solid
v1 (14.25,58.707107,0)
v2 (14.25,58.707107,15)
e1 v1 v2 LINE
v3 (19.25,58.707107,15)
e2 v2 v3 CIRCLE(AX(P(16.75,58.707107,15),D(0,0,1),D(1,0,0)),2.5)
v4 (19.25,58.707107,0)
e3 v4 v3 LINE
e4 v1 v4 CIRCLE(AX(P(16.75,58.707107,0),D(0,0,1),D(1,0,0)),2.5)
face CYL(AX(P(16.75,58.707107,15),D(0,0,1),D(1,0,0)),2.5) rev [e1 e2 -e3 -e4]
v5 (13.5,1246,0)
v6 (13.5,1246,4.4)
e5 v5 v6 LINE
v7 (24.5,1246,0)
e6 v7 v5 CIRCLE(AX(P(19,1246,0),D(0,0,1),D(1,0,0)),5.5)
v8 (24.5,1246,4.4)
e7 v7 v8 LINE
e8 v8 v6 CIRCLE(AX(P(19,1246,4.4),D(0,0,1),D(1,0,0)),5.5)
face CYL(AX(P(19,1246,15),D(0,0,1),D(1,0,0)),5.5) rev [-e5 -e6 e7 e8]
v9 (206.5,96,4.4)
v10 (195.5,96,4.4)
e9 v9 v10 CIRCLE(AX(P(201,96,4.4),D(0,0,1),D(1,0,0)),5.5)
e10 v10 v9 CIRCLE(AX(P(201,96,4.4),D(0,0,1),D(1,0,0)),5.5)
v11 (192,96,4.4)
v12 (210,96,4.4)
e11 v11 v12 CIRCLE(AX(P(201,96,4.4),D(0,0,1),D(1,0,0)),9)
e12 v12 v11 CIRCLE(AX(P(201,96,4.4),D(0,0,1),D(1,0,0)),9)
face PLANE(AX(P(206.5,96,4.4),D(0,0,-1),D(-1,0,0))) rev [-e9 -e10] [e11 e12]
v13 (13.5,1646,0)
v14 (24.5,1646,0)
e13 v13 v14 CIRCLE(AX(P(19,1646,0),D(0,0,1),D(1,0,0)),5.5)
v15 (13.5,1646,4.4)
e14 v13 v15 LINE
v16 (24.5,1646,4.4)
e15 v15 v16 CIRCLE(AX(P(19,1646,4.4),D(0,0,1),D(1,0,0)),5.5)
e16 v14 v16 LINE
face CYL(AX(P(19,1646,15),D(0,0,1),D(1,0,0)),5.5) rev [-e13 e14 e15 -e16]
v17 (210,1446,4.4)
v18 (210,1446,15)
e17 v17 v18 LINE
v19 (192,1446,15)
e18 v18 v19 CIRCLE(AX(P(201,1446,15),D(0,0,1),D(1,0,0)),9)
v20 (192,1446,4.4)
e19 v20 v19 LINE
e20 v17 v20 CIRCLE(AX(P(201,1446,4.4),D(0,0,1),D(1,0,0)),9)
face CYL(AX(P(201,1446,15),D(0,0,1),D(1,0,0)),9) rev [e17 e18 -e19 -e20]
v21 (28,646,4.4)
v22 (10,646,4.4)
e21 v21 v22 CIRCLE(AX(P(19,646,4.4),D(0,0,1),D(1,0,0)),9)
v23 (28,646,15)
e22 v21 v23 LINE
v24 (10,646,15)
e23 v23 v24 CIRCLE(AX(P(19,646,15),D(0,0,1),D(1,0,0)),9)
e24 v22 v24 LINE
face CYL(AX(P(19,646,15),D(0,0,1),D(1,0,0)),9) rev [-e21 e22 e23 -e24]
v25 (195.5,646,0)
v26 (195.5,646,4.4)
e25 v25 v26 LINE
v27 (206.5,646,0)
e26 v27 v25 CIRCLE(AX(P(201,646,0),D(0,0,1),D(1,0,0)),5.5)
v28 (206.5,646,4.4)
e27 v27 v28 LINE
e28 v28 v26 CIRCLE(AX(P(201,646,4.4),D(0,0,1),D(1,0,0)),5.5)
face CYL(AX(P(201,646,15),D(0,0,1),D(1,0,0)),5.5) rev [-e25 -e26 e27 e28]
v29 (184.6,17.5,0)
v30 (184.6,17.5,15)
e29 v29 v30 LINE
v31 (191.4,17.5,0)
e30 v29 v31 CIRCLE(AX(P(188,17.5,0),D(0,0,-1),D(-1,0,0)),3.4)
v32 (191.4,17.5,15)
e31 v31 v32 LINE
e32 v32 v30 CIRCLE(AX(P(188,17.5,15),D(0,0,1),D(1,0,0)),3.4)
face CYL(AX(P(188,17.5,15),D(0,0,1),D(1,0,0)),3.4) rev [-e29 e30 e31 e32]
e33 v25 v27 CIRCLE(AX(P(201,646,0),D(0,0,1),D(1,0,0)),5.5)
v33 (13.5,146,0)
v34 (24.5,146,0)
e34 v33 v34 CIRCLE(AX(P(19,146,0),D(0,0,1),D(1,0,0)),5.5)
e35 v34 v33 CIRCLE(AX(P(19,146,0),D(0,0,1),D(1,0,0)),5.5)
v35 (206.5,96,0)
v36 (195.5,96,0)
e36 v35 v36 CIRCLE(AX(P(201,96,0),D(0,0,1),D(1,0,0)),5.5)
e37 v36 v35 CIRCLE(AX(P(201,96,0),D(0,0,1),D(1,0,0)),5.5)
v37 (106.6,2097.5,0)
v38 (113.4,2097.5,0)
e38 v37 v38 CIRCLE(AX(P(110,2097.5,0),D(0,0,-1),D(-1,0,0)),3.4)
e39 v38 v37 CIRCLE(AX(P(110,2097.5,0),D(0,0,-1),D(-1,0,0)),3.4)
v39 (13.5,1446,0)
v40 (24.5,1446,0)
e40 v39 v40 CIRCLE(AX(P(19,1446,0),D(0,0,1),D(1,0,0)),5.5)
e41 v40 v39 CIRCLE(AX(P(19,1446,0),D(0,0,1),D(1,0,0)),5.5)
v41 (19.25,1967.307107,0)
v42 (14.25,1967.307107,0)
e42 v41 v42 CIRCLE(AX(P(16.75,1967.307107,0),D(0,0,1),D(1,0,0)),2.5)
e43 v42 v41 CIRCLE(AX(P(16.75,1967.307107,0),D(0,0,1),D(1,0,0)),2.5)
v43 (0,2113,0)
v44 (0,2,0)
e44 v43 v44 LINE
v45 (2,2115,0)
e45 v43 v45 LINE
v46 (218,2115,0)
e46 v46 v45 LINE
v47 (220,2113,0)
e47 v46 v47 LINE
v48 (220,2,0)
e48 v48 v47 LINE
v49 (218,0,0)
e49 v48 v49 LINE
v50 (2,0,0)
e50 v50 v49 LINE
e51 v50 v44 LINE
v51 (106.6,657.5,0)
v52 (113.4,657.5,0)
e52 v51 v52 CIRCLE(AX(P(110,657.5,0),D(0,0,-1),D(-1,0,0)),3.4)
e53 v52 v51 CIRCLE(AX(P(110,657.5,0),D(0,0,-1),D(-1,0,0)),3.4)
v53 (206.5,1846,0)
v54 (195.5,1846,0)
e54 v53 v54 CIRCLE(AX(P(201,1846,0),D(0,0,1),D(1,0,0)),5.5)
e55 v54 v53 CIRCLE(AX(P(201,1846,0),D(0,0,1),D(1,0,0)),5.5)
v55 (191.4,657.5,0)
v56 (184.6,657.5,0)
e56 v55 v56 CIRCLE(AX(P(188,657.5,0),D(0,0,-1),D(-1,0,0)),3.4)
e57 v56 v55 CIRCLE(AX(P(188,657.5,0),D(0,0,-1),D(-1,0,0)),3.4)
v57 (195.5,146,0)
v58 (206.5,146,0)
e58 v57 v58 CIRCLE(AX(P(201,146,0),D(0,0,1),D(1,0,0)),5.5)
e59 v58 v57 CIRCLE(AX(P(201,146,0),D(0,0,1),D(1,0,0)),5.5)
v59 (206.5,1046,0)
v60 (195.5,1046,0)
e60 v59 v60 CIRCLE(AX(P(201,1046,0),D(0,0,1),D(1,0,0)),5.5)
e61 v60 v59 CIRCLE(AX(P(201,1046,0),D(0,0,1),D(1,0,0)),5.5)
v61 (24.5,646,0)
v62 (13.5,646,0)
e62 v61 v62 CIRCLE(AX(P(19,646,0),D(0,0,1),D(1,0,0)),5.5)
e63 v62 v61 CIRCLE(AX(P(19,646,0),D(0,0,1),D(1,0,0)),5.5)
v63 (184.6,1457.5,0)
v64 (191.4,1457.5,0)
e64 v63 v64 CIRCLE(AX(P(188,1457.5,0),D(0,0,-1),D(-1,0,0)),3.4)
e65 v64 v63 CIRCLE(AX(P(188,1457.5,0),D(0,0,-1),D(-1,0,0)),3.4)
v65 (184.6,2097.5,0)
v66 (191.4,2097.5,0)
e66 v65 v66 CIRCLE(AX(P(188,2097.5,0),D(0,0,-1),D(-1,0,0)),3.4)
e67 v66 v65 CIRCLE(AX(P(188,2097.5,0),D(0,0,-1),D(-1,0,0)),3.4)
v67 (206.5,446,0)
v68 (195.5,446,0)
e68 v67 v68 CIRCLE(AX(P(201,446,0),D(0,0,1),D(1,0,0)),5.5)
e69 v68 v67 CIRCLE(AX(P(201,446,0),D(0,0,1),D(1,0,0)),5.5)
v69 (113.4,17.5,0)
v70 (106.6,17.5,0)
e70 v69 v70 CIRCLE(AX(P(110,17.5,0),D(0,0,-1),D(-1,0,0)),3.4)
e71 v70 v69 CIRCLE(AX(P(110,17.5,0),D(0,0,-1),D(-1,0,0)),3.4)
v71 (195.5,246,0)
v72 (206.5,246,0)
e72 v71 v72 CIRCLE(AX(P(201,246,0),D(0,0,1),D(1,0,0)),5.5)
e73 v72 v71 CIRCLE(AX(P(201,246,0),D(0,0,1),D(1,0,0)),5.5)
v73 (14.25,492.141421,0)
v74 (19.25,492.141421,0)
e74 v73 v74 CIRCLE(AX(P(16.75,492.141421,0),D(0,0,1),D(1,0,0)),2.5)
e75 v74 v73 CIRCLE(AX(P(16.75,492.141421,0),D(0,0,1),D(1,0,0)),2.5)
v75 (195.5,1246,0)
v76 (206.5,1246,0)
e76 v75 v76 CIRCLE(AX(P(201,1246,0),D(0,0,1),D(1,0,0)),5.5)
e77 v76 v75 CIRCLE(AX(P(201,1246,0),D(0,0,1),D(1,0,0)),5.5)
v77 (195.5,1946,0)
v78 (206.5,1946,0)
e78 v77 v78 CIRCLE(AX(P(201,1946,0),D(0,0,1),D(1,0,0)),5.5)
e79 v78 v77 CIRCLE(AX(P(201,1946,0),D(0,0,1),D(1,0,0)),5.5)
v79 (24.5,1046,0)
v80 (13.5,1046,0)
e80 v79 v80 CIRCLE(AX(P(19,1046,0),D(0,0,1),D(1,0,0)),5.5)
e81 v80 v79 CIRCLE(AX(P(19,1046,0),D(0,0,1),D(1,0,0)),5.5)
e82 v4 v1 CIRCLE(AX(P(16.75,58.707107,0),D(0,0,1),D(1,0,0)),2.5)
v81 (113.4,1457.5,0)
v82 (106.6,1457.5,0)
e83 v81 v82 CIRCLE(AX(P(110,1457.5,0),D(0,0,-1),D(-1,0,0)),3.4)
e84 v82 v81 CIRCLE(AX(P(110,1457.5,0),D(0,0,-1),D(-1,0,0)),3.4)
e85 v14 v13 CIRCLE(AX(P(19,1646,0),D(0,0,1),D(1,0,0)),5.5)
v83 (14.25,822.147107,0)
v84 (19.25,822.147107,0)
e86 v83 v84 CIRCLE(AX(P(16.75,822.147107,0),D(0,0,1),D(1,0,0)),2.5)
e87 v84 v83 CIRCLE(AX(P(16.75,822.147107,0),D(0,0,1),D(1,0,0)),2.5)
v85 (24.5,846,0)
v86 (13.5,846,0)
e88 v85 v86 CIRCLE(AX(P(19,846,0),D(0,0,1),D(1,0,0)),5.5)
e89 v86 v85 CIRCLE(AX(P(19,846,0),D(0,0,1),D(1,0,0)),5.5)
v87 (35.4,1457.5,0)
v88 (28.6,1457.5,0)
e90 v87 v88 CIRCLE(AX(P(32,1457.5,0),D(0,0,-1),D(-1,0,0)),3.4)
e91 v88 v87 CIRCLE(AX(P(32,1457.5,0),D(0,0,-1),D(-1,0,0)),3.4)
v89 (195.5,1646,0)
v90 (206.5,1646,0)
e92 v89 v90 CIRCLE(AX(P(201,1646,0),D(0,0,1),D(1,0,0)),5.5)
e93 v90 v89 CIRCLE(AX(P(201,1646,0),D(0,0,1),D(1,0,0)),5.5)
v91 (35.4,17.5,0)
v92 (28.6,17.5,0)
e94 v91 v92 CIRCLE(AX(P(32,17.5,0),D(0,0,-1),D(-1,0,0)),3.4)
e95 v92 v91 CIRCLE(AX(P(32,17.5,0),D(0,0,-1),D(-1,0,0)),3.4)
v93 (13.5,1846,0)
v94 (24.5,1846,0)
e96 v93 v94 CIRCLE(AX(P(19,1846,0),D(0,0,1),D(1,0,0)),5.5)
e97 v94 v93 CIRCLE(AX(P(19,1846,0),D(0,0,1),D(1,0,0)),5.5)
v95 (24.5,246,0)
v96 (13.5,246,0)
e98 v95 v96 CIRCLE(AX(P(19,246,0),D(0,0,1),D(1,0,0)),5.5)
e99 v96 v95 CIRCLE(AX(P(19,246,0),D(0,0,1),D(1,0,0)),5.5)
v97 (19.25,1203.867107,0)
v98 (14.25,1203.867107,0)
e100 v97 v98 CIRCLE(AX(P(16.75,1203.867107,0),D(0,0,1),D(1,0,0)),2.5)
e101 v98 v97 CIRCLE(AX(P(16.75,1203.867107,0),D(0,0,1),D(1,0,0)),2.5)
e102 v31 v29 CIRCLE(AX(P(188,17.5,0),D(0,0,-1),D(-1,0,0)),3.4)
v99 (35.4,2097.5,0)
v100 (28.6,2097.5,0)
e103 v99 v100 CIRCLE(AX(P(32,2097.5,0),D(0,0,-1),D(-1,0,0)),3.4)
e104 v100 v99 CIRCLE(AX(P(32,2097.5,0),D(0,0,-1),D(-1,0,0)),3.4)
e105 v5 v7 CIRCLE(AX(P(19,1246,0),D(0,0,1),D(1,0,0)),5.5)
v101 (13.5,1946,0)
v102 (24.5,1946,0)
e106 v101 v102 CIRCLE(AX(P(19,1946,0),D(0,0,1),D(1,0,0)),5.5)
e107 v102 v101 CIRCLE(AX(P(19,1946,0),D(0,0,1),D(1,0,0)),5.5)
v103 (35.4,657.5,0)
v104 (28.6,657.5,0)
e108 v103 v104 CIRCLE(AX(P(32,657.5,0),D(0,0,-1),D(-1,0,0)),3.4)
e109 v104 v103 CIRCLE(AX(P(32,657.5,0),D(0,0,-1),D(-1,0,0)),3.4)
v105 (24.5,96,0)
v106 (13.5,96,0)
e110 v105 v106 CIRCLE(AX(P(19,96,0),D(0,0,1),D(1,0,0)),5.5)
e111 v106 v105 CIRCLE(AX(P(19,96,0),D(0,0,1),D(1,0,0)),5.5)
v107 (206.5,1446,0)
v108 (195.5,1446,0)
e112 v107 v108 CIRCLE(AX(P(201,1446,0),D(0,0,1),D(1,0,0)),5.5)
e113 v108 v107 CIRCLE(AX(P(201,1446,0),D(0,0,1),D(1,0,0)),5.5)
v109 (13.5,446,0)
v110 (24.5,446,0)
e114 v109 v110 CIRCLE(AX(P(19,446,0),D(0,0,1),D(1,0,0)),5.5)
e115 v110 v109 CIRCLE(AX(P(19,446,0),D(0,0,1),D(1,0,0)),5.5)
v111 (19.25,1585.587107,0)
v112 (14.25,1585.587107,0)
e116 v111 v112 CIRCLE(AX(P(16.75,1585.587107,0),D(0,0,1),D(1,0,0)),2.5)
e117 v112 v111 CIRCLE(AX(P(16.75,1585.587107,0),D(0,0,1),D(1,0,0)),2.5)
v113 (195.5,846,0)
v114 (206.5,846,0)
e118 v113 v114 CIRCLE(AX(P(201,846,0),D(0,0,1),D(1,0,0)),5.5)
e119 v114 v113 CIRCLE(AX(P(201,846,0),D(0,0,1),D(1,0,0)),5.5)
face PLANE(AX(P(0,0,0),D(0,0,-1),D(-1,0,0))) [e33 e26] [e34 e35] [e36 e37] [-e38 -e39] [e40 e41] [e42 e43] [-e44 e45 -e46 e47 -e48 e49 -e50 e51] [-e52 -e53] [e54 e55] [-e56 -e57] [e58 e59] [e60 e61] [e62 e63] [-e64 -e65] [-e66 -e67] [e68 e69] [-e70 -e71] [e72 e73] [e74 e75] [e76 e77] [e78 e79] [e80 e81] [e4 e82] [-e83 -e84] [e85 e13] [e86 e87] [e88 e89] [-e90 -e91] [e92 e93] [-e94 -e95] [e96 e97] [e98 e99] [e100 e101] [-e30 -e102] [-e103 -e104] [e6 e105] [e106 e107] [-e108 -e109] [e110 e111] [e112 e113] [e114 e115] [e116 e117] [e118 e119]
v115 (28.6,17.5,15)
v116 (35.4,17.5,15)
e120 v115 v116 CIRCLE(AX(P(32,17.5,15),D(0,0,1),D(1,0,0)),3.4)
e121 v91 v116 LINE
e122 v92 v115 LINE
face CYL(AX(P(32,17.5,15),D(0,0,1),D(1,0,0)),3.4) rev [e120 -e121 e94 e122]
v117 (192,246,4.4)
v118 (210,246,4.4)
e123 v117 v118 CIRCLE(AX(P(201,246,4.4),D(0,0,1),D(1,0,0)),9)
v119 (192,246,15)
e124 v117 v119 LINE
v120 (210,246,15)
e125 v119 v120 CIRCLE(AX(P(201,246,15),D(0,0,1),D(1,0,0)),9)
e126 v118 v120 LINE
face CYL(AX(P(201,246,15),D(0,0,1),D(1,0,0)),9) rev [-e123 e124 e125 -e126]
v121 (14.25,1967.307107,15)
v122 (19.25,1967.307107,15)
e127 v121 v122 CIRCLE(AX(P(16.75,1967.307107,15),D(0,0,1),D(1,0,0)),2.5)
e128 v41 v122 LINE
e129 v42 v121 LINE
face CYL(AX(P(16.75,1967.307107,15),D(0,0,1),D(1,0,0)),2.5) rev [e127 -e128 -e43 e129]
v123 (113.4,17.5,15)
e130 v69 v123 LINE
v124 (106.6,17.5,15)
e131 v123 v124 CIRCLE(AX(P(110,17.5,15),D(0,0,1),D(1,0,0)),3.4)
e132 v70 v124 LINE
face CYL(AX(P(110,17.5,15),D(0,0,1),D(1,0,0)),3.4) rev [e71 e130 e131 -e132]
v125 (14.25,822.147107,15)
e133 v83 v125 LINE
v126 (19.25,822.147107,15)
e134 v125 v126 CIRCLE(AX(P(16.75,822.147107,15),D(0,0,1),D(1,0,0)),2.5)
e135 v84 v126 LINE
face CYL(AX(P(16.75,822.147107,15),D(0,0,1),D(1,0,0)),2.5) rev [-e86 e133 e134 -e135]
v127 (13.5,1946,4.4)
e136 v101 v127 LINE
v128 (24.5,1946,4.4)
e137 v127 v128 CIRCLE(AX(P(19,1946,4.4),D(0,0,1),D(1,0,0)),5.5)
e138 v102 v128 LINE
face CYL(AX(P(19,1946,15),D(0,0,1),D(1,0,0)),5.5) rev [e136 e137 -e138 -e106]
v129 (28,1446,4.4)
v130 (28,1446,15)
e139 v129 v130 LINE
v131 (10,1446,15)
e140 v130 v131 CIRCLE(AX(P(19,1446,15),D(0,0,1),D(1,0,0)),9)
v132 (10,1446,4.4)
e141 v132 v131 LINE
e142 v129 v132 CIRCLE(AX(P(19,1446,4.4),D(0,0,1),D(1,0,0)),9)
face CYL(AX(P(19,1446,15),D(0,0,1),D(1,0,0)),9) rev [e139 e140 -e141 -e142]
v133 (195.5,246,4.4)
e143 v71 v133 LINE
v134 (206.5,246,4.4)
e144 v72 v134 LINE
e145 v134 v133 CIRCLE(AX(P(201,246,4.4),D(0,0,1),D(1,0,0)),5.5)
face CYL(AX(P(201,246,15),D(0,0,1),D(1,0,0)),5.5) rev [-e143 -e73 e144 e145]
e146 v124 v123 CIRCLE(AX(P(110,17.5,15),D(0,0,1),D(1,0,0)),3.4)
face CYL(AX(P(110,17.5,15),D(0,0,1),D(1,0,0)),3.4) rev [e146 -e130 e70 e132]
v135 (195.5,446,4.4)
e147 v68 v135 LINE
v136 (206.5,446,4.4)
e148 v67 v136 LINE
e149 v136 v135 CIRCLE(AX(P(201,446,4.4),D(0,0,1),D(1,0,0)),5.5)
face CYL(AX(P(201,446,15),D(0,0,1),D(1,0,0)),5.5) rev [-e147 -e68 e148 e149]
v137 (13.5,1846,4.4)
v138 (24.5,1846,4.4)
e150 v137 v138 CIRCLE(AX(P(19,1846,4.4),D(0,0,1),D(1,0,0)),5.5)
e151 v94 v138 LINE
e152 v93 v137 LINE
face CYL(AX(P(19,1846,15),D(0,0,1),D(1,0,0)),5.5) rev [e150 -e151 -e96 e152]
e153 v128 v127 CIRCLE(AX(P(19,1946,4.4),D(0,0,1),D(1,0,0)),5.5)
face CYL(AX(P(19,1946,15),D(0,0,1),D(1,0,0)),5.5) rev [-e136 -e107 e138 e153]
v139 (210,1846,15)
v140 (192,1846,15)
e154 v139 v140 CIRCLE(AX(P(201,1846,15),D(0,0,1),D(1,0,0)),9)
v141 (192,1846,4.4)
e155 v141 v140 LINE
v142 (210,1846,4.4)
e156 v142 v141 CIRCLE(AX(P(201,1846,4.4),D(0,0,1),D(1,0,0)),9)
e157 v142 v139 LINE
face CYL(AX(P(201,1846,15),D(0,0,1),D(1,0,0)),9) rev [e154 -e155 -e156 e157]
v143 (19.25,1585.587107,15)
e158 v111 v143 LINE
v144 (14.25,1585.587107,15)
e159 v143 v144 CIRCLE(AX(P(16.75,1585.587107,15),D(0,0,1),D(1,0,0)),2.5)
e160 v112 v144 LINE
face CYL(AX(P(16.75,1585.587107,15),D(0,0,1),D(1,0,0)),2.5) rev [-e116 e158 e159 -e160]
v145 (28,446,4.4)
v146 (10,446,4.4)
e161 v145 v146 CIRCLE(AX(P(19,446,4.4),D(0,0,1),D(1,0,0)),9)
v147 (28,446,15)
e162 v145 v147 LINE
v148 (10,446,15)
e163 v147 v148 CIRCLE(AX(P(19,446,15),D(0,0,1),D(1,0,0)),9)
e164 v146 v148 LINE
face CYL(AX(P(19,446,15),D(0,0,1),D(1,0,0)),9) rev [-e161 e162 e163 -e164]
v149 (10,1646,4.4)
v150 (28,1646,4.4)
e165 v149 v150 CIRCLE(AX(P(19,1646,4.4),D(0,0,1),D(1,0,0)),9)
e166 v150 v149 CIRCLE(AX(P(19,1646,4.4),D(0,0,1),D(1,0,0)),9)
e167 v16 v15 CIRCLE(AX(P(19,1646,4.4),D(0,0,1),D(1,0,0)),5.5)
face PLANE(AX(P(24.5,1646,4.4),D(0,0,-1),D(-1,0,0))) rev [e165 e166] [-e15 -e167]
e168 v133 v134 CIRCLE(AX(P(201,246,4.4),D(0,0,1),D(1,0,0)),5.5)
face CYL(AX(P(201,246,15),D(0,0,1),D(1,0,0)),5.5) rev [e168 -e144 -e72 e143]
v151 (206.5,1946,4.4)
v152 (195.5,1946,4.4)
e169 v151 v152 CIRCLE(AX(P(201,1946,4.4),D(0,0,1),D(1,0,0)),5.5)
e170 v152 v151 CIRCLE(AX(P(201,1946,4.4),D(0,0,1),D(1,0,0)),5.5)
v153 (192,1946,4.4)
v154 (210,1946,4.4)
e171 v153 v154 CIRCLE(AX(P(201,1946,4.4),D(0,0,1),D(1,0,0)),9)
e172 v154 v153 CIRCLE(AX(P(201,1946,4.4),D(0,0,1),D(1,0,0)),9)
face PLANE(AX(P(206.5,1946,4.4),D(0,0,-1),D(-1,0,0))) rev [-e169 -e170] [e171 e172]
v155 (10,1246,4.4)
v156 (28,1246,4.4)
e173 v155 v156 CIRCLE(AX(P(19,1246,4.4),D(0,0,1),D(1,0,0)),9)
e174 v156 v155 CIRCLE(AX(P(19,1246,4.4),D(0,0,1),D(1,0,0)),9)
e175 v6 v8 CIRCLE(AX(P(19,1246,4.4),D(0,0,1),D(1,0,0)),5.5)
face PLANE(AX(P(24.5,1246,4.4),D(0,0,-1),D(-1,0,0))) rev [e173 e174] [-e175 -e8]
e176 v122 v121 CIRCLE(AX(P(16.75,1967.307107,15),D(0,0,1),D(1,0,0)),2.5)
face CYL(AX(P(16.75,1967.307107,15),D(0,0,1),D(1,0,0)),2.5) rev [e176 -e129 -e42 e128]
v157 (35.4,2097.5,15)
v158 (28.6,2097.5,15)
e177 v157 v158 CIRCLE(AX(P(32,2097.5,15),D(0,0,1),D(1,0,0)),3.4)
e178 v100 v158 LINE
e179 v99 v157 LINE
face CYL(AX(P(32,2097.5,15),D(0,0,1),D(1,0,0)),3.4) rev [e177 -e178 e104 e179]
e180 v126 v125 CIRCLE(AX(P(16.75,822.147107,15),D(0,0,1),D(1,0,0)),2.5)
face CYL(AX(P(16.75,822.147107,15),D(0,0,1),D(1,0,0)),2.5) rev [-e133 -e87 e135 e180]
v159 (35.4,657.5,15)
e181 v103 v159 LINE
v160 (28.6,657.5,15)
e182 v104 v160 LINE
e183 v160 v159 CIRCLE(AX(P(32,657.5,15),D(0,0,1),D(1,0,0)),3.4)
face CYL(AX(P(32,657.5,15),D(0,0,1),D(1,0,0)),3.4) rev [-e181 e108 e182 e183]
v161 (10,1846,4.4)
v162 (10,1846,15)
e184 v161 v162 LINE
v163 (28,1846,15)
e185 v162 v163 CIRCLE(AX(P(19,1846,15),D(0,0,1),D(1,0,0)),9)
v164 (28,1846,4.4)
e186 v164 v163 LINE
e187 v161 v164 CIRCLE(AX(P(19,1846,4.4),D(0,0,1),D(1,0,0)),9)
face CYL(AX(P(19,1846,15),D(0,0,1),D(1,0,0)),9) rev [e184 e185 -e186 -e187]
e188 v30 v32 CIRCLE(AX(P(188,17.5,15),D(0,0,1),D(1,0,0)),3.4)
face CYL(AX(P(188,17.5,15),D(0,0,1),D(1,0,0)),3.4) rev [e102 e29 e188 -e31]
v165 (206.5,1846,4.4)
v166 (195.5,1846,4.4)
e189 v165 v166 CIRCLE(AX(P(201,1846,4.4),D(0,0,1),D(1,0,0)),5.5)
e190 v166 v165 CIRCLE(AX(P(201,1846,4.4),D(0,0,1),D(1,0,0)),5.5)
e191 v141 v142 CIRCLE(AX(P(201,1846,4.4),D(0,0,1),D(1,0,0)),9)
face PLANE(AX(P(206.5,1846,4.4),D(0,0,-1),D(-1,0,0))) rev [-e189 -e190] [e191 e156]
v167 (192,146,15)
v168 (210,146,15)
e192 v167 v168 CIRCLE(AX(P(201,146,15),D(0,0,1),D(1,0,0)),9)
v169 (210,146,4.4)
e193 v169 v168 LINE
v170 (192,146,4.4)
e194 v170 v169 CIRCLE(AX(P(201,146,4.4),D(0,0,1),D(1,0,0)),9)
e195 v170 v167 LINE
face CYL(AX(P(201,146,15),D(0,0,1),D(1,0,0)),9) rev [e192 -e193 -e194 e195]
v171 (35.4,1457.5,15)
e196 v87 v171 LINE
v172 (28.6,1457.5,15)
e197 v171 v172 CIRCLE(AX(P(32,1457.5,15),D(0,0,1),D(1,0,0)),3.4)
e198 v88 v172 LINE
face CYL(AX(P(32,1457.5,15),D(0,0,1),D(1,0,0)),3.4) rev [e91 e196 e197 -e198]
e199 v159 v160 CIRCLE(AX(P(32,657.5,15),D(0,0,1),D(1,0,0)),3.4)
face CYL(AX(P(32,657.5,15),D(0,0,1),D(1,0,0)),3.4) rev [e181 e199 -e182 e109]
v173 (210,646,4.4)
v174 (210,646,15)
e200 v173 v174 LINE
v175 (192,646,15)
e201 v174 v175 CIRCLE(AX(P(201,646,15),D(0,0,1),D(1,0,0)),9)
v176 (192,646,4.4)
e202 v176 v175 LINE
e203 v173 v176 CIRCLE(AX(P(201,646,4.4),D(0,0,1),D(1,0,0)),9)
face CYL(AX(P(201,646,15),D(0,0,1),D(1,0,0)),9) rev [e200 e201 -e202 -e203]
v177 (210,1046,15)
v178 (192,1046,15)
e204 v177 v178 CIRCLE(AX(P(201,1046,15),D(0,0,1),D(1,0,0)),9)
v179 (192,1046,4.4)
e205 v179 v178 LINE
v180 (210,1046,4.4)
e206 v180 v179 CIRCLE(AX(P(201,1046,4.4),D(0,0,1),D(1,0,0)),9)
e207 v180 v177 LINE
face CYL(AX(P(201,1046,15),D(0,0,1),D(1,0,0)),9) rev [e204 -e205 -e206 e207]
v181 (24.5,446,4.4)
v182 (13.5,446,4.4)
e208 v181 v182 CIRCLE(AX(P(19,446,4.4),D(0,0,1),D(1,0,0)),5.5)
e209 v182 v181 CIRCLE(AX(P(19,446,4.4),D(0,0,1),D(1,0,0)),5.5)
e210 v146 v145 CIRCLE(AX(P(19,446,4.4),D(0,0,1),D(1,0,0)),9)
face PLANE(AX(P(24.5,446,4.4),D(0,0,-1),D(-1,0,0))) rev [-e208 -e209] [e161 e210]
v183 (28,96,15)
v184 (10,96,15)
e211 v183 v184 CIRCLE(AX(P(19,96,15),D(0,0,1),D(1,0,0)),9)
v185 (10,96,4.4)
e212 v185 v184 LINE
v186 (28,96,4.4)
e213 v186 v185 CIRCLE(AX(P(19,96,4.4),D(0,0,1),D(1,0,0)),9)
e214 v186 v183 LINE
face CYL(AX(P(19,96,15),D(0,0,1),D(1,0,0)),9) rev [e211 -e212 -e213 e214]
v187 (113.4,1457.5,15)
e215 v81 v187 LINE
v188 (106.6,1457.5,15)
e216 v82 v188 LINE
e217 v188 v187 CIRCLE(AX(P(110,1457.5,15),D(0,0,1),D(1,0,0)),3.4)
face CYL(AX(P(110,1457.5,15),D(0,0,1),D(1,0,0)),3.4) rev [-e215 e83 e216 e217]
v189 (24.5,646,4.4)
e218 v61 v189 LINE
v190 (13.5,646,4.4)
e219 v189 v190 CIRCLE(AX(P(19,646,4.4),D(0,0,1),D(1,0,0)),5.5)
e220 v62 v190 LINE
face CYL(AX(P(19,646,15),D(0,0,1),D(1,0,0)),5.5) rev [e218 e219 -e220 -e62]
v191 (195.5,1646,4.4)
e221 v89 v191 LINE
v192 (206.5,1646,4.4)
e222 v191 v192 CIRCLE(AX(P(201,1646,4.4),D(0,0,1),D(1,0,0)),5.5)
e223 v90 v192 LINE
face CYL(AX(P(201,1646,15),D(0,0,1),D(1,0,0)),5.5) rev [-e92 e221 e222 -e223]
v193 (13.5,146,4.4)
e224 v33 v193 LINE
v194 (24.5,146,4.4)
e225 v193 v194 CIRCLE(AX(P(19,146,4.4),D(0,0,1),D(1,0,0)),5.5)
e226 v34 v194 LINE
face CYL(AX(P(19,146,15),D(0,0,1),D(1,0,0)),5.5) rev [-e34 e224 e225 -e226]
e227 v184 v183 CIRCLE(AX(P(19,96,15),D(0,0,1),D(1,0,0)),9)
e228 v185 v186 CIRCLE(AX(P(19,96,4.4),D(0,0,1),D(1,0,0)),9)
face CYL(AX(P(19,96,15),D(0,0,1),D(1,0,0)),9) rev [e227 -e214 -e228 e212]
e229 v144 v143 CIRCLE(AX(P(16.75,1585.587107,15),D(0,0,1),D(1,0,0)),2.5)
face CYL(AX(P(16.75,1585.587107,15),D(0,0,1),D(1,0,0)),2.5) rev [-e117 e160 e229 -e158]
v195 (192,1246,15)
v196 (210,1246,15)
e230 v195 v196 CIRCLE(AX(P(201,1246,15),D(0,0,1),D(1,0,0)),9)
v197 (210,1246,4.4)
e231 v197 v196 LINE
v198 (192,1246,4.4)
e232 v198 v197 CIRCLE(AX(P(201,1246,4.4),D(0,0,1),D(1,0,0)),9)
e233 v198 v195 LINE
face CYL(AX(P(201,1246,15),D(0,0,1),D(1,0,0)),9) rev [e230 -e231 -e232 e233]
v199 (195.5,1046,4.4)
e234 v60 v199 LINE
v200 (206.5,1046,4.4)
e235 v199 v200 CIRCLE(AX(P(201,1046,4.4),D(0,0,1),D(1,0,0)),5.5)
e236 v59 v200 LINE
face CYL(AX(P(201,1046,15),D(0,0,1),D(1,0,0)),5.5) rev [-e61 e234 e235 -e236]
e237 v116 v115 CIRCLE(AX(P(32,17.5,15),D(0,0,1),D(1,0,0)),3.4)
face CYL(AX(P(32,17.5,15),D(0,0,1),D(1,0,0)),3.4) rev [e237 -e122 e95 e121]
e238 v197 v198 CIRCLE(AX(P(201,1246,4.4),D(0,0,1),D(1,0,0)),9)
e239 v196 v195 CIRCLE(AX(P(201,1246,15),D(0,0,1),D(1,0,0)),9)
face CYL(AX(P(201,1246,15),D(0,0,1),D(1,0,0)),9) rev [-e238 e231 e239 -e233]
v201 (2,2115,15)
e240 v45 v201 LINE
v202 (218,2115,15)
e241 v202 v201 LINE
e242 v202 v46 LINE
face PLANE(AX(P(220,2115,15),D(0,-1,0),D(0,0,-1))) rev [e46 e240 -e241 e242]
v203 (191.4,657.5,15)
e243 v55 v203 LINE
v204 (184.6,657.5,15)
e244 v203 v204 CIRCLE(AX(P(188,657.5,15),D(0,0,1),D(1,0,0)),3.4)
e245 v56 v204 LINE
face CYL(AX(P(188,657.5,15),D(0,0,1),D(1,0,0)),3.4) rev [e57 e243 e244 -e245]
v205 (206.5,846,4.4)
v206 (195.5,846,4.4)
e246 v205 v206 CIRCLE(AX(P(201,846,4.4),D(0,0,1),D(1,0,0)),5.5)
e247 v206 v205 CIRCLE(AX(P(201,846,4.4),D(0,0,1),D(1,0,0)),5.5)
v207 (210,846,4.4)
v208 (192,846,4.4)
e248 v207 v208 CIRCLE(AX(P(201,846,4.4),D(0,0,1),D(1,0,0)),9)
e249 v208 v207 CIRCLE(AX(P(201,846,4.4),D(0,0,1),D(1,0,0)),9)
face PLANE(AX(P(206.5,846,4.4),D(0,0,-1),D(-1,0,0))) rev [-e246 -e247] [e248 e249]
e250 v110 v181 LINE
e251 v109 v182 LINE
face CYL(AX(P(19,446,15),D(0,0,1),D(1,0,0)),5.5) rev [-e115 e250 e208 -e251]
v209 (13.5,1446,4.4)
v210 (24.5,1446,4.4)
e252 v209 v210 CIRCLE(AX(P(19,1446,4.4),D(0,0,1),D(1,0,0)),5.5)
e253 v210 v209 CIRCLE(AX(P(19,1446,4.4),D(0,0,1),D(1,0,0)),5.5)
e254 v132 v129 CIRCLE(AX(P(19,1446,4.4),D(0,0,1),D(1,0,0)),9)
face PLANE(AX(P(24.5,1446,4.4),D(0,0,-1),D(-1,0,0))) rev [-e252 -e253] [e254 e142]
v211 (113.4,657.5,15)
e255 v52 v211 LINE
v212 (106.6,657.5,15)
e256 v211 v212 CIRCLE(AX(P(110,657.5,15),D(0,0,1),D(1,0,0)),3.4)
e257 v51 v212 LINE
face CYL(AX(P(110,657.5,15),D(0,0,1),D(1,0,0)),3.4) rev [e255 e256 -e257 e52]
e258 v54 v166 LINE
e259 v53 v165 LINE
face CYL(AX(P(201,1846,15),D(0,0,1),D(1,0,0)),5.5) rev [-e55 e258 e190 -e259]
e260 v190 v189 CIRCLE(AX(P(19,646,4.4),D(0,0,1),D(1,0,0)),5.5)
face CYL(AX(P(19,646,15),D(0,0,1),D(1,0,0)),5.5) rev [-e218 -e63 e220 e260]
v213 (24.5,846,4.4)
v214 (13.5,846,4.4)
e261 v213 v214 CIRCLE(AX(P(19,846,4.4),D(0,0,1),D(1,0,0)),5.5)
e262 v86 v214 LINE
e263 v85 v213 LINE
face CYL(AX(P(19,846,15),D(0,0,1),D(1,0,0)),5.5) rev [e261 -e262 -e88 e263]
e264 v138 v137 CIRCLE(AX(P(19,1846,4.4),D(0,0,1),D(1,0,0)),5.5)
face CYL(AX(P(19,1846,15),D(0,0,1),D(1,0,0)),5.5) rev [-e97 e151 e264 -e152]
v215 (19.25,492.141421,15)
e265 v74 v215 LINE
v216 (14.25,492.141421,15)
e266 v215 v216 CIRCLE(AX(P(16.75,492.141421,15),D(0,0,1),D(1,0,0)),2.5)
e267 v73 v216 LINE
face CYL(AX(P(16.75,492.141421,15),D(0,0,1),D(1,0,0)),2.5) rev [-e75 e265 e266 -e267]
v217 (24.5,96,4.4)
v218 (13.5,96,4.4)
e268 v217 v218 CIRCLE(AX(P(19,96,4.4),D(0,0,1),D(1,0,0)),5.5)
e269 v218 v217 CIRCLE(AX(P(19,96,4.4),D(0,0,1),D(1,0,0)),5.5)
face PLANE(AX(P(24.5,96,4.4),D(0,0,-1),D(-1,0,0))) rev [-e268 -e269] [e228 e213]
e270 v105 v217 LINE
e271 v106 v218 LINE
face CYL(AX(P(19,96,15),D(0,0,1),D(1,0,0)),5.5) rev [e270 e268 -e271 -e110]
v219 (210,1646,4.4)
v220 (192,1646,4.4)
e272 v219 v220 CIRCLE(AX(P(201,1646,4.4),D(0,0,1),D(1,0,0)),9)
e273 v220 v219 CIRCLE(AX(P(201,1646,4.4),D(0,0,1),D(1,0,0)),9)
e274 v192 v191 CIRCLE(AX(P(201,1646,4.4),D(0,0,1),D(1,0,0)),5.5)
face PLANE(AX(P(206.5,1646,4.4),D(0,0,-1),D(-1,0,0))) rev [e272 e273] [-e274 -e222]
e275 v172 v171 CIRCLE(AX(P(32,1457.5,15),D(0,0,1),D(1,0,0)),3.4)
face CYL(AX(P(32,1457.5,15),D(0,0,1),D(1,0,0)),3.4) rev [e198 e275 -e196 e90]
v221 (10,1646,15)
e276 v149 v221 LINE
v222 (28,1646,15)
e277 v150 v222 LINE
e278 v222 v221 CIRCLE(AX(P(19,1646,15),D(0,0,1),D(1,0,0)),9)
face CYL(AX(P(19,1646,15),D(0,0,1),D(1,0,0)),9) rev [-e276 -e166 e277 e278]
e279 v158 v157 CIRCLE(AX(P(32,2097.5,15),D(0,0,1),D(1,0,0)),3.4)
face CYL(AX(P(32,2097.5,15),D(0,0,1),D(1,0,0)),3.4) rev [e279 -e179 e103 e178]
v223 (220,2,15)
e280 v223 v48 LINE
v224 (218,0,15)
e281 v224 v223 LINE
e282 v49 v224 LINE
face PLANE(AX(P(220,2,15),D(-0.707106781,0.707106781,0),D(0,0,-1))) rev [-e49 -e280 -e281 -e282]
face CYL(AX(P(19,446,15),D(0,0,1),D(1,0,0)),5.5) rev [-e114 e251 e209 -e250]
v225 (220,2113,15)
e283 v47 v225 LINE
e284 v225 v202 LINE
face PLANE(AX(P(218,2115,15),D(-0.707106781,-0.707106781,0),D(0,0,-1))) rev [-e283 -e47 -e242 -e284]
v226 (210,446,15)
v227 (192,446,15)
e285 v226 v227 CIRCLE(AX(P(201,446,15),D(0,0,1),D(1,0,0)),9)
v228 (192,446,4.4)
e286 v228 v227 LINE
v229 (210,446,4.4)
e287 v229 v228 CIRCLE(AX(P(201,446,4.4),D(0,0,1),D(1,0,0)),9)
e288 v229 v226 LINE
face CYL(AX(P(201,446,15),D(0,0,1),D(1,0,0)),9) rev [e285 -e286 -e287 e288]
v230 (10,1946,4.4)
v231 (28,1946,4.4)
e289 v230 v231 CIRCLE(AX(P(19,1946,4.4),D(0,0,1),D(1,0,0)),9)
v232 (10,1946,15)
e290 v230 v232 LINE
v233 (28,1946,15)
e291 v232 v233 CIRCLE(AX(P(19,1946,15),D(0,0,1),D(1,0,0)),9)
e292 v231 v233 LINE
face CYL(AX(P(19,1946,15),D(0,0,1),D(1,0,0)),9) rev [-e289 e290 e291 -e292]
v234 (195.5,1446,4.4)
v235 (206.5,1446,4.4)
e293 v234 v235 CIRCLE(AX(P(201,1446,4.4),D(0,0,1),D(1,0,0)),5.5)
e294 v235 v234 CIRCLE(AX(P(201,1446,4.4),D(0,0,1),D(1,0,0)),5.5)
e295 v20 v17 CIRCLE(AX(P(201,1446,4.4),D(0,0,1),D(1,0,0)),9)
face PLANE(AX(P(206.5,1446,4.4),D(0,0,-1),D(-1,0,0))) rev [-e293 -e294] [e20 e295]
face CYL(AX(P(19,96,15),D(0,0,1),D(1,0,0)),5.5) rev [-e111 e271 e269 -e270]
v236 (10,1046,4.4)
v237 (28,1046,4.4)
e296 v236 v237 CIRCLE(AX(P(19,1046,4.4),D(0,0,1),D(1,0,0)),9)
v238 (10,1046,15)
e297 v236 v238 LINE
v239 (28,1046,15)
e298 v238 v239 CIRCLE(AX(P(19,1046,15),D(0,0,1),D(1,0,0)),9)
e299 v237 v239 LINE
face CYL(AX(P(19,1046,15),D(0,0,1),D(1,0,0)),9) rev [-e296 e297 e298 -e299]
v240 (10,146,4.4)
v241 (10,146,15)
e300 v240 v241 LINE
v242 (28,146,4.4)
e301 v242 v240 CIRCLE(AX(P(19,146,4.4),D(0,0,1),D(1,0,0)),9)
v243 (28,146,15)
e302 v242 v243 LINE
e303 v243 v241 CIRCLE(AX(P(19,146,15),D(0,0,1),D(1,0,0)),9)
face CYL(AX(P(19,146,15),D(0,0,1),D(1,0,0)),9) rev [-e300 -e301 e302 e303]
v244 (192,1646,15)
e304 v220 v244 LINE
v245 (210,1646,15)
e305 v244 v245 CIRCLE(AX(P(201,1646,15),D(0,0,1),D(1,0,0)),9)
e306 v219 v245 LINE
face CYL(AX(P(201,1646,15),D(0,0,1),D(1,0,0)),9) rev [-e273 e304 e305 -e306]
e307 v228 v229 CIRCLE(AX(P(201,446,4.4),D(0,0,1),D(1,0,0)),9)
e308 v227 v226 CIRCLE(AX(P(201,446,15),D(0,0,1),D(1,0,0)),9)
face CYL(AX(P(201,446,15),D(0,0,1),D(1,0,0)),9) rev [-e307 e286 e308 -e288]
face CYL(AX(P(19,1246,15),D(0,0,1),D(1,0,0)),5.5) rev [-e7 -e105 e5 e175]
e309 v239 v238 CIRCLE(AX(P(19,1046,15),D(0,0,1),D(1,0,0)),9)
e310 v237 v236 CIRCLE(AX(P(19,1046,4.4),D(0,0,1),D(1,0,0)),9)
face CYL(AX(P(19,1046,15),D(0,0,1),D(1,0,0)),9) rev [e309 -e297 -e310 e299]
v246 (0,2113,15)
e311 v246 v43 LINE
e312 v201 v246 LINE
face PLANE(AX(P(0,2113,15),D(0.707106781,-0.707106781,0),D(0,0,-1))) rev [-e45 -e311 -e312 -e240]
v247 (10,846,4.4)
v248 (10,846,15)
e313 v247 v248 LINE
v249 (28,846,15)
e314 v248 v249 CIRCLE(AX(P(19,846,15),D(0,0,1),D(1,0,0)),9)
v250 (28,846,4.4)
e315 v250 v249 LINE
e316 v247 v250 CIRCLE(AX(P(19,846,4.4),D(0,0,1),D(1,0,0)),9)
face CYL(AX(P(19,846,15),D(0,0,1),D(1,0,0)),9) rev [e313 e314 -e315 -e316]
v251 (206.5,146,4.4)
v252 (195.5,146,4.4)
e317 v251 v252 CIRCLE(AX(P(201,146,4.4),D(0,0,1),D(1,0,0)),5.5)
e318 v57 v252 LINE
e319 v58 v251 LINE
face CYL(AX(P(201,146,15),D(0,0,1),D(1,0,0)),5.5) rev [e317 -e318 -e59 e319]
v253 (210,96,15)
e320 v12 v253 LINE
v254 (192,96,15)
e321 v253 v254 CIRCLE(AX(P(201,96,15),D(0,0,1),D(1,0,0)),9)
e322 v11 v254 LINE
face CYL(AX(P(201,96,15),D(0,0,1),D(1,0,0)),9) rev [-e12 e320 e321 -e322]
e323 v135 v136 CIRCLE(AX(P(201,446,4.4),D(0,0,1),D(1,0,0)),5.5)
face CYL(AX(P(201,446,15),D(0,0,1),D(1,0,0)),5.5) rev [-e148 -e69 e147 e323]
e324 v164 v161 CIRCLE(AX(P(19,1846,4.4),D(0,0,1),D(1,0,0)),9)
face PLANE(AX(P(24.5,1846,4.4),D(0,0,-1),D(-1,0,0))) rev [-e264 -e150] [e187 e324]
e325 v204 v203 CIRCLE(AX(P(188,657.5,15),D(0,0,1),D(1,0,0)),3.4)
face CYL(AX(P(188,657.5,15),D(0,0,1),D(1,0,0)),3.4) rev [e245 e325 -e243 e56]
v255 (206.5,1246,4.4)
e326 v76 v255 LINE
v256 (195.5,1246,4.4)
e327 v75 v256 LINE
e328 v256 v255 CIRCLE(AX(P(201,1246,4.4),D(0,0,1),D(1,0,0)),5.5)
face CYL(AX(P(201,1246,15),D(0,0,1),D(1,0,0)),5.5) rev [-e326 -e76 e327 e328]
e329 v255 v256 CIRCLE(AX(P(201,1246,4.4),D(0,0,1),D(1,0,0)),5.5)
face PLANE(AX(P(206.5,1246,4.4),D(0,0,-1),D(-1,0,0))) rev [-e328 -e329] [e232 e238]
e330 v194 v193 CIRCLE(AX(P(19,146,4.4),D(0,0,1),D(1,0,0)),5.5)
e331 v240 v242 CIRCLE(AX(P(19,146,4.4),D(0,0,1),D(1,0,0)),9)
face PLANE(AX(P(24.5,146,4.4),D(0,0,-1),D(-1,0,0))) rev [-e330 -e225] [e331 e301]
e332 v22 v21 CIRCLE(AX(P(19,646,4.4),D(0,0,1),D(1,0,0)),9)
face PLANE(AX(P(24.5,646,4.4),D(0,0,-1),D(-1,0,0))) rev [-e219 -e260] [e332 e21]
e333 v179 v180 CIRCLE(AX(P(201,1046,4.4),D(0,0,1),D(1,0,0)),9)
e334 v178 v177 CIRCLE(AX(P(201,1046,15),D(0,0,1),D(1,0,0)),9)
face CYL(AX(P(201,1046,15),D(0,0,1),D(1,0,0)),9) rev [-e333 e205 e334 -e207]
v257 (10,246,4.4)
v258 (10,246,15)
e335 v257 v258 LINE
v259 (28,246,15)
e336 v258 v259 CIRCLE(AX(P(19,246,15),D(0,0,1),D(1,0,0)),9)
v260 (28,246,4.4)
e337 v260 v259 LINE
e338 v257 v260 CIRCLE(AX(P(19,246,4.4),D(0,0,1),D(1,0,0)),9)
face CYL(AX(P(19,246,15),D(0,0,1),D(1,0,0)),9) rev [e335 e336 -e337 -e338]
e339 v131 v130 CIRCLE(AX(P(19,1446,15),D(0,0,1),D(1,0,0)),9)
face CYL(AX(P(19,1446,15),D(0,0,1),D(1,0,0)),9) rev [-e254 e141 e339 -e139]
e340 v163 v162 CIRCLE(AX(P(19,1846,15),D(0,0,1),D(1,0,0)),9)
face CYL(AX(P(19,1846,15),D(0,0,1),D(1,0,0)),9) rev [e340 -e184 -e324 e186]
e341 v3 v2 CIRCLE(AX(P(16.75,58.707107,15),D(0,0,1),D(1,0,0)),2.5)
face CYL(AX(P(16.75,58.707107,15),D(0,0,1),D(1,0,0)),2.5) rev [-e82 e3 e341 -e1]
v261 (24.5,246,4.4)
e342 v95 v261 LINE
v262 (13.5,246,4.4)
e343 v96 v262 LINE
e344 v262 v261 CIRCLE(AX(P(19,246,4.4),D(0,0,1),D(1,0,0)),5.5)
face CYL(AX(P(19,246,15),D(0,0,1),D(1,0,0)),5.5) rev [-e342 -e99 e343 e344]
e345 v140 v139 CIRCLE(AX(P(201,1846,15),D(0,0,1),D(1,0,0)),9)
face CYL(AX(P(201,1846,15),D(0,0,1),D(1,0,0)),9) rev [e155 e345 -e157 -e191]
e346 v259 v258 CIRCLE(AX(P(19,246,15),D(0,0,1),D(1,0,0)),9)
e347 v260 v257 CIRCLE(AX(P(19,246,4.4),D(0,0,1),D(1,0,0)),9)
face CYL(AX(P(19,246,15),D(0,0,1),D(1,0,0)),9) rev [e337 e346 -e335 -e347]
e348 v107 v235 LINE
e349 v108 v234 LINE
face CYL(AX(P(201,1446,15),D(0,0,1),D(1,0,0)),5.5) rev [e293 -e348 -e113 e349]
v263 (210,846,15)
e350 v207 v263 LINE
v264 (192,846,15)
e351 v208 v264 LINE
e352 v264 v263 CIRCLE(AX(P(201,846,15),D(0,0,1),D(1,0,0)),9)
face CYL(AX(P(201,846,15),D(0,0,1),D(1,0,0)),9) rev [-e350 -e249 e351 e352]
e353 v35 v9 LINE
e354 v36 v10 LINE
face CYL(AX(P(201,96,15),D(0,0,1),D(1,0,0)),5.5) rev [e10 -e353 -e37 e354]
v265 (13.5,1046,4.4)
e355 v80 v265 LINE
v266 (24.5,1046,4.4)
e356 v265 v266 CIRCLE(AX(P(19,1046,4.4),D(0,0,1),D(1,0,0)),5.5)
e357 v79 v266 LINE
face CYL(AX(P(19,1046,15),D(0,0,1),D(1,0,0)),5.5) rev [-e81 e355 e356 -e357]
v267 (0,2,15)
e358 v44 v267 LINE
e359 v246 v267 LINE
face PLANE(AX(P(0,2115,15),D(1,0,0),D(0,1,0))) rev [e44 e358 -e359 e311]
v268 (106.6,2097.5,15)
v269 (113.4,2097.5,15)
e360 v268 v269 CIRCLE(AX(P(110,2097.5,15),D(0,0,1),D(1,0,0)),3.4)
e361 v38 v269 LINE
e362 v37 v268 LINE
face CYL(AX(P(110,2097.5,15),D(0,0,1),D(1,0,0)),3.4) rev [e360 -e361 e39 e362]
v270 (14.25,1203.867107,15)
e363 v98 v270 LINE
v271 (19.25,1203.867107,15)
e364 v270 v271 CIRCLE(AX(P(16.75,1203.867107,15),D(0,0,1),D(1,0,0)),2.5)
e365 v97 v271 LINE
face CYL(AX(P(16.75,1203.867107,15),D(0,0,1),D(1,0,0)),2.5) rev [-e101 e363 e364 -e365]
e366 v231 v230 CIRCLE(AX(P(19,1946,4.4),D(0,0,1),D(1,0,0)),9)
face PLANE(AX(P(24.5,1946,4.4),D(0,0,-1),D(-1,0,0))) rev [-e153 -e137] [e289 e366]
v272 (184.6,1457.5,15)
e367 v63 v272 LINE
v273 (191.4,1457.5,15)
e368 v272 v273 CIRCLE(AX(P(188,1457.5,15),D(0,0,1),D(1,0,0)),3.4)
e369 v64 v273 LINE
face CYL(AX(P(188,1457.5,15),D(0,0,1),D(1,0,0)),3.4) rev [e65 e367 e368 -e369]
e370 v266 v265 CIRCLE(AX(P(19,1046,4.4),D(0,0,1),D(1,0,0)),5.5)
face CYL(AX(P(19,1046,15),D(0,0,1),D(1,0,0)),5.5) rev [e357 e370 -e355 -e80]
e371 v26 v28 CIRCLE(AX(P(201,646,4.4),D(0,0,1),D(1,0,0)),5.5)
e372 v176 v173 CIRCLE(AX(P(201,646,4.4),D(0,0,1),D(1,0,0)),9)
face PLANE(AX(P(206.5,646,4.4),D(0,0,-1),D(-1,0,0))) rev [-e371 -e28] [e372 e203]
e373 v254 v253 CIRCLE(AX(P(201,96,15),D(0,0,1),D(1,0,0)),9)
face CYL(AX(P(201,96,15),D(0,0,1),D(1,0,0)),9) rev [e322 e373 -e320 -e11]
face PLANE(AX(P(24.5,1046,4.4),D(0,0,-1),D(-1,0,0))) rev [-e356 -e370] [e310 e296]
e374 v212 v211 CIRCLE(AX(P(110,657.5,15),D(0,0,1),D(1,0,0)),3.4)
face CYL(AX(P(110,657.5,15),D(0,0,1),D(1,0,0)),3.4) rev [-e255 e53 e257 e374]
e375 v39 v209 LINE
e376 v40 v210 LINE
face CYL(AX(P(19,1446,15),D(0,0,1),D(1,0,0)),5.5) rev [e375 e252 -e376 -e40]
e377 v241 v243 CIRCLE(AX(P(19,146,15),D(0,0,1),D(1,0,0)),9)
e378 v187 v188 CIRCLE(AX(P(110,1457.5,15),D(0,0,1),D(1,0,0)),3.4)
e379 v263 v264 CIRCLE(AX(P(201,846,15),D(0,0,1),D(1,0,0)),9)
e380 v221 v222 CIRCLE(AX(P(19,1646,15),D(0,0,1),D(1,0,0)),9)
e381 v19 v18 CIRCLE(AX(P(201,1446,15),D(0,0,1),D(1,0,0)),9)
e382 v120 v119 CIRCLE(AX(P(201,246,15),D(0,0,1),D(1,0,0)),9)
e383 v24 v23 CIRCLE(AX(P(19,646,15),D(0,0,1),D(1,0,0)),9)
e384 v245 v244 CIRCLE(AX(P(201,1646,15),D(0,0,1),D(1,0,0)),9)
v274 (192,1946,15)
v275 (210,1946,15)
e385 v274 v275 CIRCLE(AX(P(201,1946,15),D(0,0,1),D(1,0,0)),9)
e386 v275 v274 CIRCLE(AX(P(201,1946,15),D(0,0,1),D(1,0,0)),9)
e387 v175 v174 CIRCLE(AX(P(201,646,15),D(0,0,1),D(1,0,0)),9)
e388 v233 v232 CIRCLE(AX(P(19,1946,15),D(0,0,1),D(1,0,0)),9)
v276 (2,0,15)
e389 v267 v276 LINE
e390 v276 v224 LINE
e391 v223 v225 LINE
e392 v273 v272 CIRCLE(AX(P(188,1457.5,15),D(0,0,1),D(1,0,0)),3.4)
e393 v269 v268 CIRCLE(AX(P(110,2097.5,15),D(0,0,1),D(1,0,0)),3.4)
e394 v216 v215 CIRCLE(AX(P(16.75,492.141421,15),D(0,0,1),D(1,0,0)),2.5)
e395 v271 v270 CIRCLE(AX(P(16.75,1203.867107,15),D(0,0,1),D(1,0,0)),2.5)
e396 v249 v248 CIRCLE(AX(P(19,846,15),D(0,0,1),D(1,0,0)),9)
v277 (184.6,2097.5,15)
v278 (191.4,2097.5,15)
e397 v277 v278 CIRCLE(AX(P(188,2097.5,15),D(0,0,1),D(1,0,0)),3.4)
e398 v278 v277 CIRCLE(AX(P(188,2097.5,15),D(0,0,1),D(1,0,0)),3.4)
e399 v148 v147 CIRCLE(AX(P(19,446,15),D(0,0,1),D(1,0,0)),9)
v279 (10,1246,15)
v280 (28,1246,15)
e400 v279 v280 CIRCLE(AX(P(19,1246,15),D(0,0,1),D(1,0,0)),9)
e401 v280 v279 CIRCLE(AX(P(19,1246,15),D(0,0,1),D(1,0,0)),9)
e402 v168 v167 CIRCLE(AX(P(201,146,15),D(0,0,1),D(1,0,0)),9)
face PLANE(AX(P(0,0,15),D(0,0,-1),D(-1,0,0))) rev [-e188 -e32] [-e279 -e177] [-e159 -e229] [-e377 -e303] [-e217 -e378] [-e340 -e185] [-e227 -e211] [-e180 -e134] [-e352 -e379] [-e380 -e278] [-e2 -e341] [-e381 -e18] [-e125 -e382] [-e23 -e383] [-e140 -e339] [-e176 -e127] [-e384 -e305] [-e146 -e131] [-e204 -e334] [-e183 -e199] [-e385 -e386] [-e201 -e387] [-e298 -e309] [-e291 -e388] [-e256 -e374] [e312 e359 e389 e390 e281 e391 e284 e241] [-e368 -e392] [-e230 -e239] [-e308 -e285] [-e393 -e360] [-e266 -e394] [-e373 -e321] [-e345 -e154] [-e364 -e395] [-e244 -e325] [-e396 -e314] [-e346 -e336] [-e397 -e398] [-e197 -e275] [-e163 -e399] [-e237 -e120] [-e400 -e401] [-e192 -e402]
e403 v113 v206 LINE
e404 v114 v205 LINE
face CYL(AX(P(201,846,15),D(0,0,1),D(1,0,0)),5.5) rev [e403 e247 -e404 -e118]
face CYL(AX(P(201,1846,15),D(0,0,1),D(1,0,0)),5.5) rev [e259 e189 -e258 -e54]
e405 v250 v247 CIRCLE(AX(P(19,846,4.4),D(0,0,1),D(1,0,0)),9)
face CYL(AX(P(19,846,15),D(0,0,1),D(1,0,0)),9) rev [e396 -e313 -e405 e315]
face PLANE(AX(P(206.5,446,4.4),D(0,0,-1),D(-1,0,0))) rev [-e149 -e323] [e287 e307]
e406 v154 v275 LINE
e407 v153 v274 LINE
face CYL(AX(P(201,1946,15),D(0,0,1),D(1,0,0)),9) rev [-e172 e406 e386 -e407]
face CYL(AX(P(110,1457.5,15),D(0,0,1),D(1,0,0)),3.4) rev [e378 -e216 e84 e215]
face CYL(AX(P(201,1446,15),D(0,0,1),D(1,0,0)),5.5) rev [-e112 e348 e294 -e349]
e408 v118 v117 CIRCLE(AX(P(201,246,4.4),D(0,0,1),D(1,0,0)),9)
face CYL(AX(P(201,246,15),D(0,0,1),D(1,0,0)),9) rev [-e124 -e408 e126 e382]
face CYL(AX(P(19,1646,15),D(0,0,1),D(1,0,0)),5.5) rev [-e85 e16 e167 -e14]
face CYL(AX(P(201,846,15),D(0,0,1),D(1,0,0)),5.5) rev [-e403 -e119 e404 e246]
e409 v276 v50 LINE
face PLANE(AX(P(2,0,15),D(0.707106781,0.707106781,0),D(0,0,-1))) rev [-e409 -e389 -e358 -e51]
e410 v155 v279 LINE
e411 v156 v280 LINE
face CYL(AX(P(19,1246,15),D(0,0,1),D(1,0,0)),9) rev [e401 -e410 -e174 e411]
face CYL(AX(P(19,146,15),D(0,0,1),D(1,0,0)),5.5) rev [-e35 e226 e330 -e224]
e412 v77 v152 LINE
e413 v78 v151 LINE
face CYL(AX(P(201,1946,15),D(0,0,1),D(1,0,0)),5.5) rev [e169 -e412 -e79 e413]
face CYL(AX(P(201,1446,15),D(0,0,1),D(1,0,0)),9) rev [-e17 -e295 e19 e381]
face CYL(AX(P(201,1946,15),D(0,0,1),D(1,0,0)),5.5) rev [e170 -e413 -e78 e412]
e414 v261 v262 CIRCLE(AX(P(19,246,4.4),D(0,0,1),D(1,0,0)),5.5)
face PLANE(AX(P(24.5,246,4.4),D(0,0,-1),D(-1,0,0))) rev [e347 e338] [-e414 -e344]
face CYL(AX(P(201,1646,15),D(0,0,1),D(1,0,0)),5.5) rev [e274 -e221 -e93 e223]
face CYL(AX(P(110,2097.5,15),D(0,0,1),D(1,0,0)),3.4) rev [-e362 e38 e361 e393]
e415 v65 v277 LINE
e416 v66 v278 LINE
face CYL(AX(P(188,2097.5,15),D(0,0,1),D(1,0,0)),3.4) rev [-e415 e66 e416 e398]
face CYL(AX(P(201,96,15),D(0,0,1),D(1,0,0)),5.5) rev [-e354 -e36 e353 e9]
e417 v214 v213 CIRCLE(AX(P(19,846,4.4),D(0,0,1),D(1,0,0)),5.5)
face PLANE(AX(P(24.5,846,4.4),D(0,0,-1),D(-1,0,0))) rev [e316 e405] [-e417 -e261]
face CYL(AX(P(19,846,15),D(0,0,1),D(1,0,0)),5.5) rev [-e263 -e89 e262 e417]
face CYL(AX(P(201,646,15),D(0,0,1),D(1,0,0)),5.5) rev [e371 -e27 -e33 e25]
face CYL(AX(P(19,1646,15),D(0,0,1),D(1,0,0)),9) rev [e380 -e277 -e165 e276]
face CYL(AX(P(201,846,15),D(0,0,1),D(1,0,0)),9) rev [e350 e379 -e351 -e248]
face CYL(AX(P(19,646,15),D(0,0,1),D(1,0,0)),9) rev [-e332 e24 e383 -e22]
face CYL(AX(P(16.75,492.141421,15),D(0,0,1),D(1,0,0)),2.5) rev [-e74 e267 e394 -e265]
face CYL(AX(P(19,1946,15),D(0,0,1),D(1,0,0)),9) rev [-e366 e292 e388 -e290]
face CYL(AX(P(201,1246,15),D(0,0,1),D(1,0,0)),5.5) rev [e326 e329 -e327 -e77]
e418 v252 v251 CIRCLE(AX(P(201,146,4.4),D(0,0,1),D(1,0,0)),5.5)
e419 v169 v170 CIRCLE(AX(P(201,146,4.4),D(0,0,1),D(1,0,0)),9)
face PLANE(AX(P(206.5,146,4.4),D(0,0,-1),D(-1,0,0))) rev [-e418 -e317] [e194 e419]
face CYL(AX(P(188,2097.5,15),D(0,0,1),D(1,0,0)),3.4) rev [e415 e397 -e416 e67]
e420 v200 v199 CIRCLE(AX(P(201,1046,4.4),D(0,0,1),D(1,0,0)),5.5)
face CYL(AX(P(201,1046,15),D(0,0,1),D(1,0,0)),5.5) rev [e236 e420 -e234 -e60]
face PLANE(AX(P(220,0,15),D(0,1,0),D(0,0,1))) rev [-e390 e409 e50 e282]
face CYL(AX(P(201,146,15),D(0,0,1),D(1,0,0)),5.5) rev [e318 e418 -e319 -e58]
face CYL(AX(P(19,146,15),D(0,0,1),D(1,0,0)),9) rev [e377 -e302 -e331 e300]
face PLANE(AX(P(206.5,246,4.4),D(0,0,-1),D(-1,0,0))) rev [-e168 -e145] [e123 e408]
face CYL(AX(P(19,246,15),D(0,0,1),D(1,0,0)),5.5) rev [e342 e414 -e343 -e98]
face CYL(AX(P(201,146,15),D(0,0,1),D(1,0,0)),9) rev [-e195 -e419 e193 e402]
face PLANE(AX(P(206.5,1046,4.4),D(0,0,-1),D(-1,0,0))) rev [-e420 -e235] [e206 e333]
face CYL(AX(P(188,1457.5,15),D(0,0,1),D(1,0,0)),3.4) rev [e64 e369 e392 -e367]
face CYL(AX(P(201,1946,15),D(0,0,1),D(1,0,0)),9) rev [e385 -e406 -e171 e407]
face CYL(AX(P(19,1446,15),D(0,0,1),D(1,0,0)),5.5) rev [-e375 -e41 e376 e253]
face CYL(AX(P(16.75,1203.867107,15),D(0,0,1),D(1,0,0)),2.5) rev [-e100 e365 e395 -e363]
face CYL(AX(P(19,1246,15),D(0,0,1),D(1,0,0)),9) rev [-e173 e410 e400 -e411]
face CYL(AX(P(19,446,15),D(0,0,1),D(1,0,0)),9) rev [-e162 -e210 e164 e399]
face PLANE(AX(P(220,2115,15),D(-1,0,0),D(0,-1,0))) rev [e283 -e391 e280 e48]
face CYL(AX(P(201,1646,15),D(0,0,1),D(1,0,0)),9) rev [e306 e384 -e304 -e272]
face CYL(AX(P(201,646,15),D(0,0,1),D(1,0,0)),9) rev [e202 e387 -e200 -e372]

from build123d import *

# Parameters (mm, degrees)
SKETCH_1_W                    = 220
SKETCH_1_H                    = 2115
EXTRUDE_1_DEPTH               = 15
CHAMFER_1_SIZE                = 2
HOLE_WIZARD_M8_1_D            = 6.8
HOLE_WIZARD_M8_1_DEPTH        = 22.25
HOLE_WIZARD_M8_1_TIP          = 2.042926105
HOLE_WIZARD_M10_1_D           = 11
HOLE_WIZARD_M10_1_CBORE_D     = 18
HOLE_WIZARD_M10_1_CBORE_DEPTH = 10.6
HOLE_WIZARD_M6_2_D            = 5


with BuildPart() as part:
    # 草图1 → 凸台-拉伸1 (new body)
    with BuildSketch(Plane.XY):
        with Locations((110, 1057.5)):
            Rectangle(SKETCH_1_W, SKETCH_1_H)
    extrude(amount=EXTRUDE_1_DEPTH)

    # 倒角1
    chamfer_1_edges = [part.edges().sort_by_distance(p)[0] for p in [
        (220, 0, 7.5),
        (0, 0, 7.5),
        (0, 2115, 7.5),
        (220, 2115, 7.5),
    ]]
    chamfer(chamfer_1_edges, length=CHAMFER_1_SIZE)

    # M8 螺纹孔1
    with Locations(Plane.XY.offset(15)):
        with Locations((32, 2097.5), (32, 1457.5), (32, 657.5), (32, 17.5), (110, 2097.5), (110, 1457.5), (110, 657.5), (110, 17.5), (188, 2097.5), (188, 1457.5), (188, 657.5), (188, 17.5)):
            Hole(HOLE_WIZARD_M8_1_D / 2, depth=HOLE_WIZARD_M8_1_DEPTH)
            with Locations((0, 0, -(HOLE_WIZARD_M8_1_DEPTH + HOLE_WIZARD_M8_1_TIP / 2))):  # 118° drill point
                Cone(0, HOLE_WIZARD_M8_1_D / 2, HOLE_WIZARD_M8_1_TIP, mode=Mode.SUBTRACT)

    # M10 六角凹头螺钉的柱形沉头孔1 (through all)
    with Locations(Plane.XY.offset(15)):
        with Locations((19, 1946), (201, 1946), (19, 1846), (201, 1846), (19, 1646), (201, 1646), (19, 1446), (201, 1446), (19, 1246), (201, 1246), (19, 1046), (201, 1046), (19, 846), (201, 846), (19, 646), (201, 646), (19, 446), (201, 446), (19, 246), (201, 246), (19, 146), (201, 146), (19, 96), (201, 96)):
            CounterBoreHole(HOLE_WIZARD_M10_1_D / 2, HOLE_WIZARD_M10_1_CBORE_D / 2, HOLE_WIZARD_M10_1_CBORE_DEPTH)

    # M6 螺纹孔2 (through all)
    with Locations(Plane.XY.offset(15)):
        with Locations((16.75, 58.707106781), (16.75, 492.141421356), (16.75, 822.147106781), (16.75, 1203.867106781), (16.75, 1585.587106781), (16.75, 1967.307106781)):
            Hole(HOLE_WIZARD_M6_2_D / 2)


solid = part.part
